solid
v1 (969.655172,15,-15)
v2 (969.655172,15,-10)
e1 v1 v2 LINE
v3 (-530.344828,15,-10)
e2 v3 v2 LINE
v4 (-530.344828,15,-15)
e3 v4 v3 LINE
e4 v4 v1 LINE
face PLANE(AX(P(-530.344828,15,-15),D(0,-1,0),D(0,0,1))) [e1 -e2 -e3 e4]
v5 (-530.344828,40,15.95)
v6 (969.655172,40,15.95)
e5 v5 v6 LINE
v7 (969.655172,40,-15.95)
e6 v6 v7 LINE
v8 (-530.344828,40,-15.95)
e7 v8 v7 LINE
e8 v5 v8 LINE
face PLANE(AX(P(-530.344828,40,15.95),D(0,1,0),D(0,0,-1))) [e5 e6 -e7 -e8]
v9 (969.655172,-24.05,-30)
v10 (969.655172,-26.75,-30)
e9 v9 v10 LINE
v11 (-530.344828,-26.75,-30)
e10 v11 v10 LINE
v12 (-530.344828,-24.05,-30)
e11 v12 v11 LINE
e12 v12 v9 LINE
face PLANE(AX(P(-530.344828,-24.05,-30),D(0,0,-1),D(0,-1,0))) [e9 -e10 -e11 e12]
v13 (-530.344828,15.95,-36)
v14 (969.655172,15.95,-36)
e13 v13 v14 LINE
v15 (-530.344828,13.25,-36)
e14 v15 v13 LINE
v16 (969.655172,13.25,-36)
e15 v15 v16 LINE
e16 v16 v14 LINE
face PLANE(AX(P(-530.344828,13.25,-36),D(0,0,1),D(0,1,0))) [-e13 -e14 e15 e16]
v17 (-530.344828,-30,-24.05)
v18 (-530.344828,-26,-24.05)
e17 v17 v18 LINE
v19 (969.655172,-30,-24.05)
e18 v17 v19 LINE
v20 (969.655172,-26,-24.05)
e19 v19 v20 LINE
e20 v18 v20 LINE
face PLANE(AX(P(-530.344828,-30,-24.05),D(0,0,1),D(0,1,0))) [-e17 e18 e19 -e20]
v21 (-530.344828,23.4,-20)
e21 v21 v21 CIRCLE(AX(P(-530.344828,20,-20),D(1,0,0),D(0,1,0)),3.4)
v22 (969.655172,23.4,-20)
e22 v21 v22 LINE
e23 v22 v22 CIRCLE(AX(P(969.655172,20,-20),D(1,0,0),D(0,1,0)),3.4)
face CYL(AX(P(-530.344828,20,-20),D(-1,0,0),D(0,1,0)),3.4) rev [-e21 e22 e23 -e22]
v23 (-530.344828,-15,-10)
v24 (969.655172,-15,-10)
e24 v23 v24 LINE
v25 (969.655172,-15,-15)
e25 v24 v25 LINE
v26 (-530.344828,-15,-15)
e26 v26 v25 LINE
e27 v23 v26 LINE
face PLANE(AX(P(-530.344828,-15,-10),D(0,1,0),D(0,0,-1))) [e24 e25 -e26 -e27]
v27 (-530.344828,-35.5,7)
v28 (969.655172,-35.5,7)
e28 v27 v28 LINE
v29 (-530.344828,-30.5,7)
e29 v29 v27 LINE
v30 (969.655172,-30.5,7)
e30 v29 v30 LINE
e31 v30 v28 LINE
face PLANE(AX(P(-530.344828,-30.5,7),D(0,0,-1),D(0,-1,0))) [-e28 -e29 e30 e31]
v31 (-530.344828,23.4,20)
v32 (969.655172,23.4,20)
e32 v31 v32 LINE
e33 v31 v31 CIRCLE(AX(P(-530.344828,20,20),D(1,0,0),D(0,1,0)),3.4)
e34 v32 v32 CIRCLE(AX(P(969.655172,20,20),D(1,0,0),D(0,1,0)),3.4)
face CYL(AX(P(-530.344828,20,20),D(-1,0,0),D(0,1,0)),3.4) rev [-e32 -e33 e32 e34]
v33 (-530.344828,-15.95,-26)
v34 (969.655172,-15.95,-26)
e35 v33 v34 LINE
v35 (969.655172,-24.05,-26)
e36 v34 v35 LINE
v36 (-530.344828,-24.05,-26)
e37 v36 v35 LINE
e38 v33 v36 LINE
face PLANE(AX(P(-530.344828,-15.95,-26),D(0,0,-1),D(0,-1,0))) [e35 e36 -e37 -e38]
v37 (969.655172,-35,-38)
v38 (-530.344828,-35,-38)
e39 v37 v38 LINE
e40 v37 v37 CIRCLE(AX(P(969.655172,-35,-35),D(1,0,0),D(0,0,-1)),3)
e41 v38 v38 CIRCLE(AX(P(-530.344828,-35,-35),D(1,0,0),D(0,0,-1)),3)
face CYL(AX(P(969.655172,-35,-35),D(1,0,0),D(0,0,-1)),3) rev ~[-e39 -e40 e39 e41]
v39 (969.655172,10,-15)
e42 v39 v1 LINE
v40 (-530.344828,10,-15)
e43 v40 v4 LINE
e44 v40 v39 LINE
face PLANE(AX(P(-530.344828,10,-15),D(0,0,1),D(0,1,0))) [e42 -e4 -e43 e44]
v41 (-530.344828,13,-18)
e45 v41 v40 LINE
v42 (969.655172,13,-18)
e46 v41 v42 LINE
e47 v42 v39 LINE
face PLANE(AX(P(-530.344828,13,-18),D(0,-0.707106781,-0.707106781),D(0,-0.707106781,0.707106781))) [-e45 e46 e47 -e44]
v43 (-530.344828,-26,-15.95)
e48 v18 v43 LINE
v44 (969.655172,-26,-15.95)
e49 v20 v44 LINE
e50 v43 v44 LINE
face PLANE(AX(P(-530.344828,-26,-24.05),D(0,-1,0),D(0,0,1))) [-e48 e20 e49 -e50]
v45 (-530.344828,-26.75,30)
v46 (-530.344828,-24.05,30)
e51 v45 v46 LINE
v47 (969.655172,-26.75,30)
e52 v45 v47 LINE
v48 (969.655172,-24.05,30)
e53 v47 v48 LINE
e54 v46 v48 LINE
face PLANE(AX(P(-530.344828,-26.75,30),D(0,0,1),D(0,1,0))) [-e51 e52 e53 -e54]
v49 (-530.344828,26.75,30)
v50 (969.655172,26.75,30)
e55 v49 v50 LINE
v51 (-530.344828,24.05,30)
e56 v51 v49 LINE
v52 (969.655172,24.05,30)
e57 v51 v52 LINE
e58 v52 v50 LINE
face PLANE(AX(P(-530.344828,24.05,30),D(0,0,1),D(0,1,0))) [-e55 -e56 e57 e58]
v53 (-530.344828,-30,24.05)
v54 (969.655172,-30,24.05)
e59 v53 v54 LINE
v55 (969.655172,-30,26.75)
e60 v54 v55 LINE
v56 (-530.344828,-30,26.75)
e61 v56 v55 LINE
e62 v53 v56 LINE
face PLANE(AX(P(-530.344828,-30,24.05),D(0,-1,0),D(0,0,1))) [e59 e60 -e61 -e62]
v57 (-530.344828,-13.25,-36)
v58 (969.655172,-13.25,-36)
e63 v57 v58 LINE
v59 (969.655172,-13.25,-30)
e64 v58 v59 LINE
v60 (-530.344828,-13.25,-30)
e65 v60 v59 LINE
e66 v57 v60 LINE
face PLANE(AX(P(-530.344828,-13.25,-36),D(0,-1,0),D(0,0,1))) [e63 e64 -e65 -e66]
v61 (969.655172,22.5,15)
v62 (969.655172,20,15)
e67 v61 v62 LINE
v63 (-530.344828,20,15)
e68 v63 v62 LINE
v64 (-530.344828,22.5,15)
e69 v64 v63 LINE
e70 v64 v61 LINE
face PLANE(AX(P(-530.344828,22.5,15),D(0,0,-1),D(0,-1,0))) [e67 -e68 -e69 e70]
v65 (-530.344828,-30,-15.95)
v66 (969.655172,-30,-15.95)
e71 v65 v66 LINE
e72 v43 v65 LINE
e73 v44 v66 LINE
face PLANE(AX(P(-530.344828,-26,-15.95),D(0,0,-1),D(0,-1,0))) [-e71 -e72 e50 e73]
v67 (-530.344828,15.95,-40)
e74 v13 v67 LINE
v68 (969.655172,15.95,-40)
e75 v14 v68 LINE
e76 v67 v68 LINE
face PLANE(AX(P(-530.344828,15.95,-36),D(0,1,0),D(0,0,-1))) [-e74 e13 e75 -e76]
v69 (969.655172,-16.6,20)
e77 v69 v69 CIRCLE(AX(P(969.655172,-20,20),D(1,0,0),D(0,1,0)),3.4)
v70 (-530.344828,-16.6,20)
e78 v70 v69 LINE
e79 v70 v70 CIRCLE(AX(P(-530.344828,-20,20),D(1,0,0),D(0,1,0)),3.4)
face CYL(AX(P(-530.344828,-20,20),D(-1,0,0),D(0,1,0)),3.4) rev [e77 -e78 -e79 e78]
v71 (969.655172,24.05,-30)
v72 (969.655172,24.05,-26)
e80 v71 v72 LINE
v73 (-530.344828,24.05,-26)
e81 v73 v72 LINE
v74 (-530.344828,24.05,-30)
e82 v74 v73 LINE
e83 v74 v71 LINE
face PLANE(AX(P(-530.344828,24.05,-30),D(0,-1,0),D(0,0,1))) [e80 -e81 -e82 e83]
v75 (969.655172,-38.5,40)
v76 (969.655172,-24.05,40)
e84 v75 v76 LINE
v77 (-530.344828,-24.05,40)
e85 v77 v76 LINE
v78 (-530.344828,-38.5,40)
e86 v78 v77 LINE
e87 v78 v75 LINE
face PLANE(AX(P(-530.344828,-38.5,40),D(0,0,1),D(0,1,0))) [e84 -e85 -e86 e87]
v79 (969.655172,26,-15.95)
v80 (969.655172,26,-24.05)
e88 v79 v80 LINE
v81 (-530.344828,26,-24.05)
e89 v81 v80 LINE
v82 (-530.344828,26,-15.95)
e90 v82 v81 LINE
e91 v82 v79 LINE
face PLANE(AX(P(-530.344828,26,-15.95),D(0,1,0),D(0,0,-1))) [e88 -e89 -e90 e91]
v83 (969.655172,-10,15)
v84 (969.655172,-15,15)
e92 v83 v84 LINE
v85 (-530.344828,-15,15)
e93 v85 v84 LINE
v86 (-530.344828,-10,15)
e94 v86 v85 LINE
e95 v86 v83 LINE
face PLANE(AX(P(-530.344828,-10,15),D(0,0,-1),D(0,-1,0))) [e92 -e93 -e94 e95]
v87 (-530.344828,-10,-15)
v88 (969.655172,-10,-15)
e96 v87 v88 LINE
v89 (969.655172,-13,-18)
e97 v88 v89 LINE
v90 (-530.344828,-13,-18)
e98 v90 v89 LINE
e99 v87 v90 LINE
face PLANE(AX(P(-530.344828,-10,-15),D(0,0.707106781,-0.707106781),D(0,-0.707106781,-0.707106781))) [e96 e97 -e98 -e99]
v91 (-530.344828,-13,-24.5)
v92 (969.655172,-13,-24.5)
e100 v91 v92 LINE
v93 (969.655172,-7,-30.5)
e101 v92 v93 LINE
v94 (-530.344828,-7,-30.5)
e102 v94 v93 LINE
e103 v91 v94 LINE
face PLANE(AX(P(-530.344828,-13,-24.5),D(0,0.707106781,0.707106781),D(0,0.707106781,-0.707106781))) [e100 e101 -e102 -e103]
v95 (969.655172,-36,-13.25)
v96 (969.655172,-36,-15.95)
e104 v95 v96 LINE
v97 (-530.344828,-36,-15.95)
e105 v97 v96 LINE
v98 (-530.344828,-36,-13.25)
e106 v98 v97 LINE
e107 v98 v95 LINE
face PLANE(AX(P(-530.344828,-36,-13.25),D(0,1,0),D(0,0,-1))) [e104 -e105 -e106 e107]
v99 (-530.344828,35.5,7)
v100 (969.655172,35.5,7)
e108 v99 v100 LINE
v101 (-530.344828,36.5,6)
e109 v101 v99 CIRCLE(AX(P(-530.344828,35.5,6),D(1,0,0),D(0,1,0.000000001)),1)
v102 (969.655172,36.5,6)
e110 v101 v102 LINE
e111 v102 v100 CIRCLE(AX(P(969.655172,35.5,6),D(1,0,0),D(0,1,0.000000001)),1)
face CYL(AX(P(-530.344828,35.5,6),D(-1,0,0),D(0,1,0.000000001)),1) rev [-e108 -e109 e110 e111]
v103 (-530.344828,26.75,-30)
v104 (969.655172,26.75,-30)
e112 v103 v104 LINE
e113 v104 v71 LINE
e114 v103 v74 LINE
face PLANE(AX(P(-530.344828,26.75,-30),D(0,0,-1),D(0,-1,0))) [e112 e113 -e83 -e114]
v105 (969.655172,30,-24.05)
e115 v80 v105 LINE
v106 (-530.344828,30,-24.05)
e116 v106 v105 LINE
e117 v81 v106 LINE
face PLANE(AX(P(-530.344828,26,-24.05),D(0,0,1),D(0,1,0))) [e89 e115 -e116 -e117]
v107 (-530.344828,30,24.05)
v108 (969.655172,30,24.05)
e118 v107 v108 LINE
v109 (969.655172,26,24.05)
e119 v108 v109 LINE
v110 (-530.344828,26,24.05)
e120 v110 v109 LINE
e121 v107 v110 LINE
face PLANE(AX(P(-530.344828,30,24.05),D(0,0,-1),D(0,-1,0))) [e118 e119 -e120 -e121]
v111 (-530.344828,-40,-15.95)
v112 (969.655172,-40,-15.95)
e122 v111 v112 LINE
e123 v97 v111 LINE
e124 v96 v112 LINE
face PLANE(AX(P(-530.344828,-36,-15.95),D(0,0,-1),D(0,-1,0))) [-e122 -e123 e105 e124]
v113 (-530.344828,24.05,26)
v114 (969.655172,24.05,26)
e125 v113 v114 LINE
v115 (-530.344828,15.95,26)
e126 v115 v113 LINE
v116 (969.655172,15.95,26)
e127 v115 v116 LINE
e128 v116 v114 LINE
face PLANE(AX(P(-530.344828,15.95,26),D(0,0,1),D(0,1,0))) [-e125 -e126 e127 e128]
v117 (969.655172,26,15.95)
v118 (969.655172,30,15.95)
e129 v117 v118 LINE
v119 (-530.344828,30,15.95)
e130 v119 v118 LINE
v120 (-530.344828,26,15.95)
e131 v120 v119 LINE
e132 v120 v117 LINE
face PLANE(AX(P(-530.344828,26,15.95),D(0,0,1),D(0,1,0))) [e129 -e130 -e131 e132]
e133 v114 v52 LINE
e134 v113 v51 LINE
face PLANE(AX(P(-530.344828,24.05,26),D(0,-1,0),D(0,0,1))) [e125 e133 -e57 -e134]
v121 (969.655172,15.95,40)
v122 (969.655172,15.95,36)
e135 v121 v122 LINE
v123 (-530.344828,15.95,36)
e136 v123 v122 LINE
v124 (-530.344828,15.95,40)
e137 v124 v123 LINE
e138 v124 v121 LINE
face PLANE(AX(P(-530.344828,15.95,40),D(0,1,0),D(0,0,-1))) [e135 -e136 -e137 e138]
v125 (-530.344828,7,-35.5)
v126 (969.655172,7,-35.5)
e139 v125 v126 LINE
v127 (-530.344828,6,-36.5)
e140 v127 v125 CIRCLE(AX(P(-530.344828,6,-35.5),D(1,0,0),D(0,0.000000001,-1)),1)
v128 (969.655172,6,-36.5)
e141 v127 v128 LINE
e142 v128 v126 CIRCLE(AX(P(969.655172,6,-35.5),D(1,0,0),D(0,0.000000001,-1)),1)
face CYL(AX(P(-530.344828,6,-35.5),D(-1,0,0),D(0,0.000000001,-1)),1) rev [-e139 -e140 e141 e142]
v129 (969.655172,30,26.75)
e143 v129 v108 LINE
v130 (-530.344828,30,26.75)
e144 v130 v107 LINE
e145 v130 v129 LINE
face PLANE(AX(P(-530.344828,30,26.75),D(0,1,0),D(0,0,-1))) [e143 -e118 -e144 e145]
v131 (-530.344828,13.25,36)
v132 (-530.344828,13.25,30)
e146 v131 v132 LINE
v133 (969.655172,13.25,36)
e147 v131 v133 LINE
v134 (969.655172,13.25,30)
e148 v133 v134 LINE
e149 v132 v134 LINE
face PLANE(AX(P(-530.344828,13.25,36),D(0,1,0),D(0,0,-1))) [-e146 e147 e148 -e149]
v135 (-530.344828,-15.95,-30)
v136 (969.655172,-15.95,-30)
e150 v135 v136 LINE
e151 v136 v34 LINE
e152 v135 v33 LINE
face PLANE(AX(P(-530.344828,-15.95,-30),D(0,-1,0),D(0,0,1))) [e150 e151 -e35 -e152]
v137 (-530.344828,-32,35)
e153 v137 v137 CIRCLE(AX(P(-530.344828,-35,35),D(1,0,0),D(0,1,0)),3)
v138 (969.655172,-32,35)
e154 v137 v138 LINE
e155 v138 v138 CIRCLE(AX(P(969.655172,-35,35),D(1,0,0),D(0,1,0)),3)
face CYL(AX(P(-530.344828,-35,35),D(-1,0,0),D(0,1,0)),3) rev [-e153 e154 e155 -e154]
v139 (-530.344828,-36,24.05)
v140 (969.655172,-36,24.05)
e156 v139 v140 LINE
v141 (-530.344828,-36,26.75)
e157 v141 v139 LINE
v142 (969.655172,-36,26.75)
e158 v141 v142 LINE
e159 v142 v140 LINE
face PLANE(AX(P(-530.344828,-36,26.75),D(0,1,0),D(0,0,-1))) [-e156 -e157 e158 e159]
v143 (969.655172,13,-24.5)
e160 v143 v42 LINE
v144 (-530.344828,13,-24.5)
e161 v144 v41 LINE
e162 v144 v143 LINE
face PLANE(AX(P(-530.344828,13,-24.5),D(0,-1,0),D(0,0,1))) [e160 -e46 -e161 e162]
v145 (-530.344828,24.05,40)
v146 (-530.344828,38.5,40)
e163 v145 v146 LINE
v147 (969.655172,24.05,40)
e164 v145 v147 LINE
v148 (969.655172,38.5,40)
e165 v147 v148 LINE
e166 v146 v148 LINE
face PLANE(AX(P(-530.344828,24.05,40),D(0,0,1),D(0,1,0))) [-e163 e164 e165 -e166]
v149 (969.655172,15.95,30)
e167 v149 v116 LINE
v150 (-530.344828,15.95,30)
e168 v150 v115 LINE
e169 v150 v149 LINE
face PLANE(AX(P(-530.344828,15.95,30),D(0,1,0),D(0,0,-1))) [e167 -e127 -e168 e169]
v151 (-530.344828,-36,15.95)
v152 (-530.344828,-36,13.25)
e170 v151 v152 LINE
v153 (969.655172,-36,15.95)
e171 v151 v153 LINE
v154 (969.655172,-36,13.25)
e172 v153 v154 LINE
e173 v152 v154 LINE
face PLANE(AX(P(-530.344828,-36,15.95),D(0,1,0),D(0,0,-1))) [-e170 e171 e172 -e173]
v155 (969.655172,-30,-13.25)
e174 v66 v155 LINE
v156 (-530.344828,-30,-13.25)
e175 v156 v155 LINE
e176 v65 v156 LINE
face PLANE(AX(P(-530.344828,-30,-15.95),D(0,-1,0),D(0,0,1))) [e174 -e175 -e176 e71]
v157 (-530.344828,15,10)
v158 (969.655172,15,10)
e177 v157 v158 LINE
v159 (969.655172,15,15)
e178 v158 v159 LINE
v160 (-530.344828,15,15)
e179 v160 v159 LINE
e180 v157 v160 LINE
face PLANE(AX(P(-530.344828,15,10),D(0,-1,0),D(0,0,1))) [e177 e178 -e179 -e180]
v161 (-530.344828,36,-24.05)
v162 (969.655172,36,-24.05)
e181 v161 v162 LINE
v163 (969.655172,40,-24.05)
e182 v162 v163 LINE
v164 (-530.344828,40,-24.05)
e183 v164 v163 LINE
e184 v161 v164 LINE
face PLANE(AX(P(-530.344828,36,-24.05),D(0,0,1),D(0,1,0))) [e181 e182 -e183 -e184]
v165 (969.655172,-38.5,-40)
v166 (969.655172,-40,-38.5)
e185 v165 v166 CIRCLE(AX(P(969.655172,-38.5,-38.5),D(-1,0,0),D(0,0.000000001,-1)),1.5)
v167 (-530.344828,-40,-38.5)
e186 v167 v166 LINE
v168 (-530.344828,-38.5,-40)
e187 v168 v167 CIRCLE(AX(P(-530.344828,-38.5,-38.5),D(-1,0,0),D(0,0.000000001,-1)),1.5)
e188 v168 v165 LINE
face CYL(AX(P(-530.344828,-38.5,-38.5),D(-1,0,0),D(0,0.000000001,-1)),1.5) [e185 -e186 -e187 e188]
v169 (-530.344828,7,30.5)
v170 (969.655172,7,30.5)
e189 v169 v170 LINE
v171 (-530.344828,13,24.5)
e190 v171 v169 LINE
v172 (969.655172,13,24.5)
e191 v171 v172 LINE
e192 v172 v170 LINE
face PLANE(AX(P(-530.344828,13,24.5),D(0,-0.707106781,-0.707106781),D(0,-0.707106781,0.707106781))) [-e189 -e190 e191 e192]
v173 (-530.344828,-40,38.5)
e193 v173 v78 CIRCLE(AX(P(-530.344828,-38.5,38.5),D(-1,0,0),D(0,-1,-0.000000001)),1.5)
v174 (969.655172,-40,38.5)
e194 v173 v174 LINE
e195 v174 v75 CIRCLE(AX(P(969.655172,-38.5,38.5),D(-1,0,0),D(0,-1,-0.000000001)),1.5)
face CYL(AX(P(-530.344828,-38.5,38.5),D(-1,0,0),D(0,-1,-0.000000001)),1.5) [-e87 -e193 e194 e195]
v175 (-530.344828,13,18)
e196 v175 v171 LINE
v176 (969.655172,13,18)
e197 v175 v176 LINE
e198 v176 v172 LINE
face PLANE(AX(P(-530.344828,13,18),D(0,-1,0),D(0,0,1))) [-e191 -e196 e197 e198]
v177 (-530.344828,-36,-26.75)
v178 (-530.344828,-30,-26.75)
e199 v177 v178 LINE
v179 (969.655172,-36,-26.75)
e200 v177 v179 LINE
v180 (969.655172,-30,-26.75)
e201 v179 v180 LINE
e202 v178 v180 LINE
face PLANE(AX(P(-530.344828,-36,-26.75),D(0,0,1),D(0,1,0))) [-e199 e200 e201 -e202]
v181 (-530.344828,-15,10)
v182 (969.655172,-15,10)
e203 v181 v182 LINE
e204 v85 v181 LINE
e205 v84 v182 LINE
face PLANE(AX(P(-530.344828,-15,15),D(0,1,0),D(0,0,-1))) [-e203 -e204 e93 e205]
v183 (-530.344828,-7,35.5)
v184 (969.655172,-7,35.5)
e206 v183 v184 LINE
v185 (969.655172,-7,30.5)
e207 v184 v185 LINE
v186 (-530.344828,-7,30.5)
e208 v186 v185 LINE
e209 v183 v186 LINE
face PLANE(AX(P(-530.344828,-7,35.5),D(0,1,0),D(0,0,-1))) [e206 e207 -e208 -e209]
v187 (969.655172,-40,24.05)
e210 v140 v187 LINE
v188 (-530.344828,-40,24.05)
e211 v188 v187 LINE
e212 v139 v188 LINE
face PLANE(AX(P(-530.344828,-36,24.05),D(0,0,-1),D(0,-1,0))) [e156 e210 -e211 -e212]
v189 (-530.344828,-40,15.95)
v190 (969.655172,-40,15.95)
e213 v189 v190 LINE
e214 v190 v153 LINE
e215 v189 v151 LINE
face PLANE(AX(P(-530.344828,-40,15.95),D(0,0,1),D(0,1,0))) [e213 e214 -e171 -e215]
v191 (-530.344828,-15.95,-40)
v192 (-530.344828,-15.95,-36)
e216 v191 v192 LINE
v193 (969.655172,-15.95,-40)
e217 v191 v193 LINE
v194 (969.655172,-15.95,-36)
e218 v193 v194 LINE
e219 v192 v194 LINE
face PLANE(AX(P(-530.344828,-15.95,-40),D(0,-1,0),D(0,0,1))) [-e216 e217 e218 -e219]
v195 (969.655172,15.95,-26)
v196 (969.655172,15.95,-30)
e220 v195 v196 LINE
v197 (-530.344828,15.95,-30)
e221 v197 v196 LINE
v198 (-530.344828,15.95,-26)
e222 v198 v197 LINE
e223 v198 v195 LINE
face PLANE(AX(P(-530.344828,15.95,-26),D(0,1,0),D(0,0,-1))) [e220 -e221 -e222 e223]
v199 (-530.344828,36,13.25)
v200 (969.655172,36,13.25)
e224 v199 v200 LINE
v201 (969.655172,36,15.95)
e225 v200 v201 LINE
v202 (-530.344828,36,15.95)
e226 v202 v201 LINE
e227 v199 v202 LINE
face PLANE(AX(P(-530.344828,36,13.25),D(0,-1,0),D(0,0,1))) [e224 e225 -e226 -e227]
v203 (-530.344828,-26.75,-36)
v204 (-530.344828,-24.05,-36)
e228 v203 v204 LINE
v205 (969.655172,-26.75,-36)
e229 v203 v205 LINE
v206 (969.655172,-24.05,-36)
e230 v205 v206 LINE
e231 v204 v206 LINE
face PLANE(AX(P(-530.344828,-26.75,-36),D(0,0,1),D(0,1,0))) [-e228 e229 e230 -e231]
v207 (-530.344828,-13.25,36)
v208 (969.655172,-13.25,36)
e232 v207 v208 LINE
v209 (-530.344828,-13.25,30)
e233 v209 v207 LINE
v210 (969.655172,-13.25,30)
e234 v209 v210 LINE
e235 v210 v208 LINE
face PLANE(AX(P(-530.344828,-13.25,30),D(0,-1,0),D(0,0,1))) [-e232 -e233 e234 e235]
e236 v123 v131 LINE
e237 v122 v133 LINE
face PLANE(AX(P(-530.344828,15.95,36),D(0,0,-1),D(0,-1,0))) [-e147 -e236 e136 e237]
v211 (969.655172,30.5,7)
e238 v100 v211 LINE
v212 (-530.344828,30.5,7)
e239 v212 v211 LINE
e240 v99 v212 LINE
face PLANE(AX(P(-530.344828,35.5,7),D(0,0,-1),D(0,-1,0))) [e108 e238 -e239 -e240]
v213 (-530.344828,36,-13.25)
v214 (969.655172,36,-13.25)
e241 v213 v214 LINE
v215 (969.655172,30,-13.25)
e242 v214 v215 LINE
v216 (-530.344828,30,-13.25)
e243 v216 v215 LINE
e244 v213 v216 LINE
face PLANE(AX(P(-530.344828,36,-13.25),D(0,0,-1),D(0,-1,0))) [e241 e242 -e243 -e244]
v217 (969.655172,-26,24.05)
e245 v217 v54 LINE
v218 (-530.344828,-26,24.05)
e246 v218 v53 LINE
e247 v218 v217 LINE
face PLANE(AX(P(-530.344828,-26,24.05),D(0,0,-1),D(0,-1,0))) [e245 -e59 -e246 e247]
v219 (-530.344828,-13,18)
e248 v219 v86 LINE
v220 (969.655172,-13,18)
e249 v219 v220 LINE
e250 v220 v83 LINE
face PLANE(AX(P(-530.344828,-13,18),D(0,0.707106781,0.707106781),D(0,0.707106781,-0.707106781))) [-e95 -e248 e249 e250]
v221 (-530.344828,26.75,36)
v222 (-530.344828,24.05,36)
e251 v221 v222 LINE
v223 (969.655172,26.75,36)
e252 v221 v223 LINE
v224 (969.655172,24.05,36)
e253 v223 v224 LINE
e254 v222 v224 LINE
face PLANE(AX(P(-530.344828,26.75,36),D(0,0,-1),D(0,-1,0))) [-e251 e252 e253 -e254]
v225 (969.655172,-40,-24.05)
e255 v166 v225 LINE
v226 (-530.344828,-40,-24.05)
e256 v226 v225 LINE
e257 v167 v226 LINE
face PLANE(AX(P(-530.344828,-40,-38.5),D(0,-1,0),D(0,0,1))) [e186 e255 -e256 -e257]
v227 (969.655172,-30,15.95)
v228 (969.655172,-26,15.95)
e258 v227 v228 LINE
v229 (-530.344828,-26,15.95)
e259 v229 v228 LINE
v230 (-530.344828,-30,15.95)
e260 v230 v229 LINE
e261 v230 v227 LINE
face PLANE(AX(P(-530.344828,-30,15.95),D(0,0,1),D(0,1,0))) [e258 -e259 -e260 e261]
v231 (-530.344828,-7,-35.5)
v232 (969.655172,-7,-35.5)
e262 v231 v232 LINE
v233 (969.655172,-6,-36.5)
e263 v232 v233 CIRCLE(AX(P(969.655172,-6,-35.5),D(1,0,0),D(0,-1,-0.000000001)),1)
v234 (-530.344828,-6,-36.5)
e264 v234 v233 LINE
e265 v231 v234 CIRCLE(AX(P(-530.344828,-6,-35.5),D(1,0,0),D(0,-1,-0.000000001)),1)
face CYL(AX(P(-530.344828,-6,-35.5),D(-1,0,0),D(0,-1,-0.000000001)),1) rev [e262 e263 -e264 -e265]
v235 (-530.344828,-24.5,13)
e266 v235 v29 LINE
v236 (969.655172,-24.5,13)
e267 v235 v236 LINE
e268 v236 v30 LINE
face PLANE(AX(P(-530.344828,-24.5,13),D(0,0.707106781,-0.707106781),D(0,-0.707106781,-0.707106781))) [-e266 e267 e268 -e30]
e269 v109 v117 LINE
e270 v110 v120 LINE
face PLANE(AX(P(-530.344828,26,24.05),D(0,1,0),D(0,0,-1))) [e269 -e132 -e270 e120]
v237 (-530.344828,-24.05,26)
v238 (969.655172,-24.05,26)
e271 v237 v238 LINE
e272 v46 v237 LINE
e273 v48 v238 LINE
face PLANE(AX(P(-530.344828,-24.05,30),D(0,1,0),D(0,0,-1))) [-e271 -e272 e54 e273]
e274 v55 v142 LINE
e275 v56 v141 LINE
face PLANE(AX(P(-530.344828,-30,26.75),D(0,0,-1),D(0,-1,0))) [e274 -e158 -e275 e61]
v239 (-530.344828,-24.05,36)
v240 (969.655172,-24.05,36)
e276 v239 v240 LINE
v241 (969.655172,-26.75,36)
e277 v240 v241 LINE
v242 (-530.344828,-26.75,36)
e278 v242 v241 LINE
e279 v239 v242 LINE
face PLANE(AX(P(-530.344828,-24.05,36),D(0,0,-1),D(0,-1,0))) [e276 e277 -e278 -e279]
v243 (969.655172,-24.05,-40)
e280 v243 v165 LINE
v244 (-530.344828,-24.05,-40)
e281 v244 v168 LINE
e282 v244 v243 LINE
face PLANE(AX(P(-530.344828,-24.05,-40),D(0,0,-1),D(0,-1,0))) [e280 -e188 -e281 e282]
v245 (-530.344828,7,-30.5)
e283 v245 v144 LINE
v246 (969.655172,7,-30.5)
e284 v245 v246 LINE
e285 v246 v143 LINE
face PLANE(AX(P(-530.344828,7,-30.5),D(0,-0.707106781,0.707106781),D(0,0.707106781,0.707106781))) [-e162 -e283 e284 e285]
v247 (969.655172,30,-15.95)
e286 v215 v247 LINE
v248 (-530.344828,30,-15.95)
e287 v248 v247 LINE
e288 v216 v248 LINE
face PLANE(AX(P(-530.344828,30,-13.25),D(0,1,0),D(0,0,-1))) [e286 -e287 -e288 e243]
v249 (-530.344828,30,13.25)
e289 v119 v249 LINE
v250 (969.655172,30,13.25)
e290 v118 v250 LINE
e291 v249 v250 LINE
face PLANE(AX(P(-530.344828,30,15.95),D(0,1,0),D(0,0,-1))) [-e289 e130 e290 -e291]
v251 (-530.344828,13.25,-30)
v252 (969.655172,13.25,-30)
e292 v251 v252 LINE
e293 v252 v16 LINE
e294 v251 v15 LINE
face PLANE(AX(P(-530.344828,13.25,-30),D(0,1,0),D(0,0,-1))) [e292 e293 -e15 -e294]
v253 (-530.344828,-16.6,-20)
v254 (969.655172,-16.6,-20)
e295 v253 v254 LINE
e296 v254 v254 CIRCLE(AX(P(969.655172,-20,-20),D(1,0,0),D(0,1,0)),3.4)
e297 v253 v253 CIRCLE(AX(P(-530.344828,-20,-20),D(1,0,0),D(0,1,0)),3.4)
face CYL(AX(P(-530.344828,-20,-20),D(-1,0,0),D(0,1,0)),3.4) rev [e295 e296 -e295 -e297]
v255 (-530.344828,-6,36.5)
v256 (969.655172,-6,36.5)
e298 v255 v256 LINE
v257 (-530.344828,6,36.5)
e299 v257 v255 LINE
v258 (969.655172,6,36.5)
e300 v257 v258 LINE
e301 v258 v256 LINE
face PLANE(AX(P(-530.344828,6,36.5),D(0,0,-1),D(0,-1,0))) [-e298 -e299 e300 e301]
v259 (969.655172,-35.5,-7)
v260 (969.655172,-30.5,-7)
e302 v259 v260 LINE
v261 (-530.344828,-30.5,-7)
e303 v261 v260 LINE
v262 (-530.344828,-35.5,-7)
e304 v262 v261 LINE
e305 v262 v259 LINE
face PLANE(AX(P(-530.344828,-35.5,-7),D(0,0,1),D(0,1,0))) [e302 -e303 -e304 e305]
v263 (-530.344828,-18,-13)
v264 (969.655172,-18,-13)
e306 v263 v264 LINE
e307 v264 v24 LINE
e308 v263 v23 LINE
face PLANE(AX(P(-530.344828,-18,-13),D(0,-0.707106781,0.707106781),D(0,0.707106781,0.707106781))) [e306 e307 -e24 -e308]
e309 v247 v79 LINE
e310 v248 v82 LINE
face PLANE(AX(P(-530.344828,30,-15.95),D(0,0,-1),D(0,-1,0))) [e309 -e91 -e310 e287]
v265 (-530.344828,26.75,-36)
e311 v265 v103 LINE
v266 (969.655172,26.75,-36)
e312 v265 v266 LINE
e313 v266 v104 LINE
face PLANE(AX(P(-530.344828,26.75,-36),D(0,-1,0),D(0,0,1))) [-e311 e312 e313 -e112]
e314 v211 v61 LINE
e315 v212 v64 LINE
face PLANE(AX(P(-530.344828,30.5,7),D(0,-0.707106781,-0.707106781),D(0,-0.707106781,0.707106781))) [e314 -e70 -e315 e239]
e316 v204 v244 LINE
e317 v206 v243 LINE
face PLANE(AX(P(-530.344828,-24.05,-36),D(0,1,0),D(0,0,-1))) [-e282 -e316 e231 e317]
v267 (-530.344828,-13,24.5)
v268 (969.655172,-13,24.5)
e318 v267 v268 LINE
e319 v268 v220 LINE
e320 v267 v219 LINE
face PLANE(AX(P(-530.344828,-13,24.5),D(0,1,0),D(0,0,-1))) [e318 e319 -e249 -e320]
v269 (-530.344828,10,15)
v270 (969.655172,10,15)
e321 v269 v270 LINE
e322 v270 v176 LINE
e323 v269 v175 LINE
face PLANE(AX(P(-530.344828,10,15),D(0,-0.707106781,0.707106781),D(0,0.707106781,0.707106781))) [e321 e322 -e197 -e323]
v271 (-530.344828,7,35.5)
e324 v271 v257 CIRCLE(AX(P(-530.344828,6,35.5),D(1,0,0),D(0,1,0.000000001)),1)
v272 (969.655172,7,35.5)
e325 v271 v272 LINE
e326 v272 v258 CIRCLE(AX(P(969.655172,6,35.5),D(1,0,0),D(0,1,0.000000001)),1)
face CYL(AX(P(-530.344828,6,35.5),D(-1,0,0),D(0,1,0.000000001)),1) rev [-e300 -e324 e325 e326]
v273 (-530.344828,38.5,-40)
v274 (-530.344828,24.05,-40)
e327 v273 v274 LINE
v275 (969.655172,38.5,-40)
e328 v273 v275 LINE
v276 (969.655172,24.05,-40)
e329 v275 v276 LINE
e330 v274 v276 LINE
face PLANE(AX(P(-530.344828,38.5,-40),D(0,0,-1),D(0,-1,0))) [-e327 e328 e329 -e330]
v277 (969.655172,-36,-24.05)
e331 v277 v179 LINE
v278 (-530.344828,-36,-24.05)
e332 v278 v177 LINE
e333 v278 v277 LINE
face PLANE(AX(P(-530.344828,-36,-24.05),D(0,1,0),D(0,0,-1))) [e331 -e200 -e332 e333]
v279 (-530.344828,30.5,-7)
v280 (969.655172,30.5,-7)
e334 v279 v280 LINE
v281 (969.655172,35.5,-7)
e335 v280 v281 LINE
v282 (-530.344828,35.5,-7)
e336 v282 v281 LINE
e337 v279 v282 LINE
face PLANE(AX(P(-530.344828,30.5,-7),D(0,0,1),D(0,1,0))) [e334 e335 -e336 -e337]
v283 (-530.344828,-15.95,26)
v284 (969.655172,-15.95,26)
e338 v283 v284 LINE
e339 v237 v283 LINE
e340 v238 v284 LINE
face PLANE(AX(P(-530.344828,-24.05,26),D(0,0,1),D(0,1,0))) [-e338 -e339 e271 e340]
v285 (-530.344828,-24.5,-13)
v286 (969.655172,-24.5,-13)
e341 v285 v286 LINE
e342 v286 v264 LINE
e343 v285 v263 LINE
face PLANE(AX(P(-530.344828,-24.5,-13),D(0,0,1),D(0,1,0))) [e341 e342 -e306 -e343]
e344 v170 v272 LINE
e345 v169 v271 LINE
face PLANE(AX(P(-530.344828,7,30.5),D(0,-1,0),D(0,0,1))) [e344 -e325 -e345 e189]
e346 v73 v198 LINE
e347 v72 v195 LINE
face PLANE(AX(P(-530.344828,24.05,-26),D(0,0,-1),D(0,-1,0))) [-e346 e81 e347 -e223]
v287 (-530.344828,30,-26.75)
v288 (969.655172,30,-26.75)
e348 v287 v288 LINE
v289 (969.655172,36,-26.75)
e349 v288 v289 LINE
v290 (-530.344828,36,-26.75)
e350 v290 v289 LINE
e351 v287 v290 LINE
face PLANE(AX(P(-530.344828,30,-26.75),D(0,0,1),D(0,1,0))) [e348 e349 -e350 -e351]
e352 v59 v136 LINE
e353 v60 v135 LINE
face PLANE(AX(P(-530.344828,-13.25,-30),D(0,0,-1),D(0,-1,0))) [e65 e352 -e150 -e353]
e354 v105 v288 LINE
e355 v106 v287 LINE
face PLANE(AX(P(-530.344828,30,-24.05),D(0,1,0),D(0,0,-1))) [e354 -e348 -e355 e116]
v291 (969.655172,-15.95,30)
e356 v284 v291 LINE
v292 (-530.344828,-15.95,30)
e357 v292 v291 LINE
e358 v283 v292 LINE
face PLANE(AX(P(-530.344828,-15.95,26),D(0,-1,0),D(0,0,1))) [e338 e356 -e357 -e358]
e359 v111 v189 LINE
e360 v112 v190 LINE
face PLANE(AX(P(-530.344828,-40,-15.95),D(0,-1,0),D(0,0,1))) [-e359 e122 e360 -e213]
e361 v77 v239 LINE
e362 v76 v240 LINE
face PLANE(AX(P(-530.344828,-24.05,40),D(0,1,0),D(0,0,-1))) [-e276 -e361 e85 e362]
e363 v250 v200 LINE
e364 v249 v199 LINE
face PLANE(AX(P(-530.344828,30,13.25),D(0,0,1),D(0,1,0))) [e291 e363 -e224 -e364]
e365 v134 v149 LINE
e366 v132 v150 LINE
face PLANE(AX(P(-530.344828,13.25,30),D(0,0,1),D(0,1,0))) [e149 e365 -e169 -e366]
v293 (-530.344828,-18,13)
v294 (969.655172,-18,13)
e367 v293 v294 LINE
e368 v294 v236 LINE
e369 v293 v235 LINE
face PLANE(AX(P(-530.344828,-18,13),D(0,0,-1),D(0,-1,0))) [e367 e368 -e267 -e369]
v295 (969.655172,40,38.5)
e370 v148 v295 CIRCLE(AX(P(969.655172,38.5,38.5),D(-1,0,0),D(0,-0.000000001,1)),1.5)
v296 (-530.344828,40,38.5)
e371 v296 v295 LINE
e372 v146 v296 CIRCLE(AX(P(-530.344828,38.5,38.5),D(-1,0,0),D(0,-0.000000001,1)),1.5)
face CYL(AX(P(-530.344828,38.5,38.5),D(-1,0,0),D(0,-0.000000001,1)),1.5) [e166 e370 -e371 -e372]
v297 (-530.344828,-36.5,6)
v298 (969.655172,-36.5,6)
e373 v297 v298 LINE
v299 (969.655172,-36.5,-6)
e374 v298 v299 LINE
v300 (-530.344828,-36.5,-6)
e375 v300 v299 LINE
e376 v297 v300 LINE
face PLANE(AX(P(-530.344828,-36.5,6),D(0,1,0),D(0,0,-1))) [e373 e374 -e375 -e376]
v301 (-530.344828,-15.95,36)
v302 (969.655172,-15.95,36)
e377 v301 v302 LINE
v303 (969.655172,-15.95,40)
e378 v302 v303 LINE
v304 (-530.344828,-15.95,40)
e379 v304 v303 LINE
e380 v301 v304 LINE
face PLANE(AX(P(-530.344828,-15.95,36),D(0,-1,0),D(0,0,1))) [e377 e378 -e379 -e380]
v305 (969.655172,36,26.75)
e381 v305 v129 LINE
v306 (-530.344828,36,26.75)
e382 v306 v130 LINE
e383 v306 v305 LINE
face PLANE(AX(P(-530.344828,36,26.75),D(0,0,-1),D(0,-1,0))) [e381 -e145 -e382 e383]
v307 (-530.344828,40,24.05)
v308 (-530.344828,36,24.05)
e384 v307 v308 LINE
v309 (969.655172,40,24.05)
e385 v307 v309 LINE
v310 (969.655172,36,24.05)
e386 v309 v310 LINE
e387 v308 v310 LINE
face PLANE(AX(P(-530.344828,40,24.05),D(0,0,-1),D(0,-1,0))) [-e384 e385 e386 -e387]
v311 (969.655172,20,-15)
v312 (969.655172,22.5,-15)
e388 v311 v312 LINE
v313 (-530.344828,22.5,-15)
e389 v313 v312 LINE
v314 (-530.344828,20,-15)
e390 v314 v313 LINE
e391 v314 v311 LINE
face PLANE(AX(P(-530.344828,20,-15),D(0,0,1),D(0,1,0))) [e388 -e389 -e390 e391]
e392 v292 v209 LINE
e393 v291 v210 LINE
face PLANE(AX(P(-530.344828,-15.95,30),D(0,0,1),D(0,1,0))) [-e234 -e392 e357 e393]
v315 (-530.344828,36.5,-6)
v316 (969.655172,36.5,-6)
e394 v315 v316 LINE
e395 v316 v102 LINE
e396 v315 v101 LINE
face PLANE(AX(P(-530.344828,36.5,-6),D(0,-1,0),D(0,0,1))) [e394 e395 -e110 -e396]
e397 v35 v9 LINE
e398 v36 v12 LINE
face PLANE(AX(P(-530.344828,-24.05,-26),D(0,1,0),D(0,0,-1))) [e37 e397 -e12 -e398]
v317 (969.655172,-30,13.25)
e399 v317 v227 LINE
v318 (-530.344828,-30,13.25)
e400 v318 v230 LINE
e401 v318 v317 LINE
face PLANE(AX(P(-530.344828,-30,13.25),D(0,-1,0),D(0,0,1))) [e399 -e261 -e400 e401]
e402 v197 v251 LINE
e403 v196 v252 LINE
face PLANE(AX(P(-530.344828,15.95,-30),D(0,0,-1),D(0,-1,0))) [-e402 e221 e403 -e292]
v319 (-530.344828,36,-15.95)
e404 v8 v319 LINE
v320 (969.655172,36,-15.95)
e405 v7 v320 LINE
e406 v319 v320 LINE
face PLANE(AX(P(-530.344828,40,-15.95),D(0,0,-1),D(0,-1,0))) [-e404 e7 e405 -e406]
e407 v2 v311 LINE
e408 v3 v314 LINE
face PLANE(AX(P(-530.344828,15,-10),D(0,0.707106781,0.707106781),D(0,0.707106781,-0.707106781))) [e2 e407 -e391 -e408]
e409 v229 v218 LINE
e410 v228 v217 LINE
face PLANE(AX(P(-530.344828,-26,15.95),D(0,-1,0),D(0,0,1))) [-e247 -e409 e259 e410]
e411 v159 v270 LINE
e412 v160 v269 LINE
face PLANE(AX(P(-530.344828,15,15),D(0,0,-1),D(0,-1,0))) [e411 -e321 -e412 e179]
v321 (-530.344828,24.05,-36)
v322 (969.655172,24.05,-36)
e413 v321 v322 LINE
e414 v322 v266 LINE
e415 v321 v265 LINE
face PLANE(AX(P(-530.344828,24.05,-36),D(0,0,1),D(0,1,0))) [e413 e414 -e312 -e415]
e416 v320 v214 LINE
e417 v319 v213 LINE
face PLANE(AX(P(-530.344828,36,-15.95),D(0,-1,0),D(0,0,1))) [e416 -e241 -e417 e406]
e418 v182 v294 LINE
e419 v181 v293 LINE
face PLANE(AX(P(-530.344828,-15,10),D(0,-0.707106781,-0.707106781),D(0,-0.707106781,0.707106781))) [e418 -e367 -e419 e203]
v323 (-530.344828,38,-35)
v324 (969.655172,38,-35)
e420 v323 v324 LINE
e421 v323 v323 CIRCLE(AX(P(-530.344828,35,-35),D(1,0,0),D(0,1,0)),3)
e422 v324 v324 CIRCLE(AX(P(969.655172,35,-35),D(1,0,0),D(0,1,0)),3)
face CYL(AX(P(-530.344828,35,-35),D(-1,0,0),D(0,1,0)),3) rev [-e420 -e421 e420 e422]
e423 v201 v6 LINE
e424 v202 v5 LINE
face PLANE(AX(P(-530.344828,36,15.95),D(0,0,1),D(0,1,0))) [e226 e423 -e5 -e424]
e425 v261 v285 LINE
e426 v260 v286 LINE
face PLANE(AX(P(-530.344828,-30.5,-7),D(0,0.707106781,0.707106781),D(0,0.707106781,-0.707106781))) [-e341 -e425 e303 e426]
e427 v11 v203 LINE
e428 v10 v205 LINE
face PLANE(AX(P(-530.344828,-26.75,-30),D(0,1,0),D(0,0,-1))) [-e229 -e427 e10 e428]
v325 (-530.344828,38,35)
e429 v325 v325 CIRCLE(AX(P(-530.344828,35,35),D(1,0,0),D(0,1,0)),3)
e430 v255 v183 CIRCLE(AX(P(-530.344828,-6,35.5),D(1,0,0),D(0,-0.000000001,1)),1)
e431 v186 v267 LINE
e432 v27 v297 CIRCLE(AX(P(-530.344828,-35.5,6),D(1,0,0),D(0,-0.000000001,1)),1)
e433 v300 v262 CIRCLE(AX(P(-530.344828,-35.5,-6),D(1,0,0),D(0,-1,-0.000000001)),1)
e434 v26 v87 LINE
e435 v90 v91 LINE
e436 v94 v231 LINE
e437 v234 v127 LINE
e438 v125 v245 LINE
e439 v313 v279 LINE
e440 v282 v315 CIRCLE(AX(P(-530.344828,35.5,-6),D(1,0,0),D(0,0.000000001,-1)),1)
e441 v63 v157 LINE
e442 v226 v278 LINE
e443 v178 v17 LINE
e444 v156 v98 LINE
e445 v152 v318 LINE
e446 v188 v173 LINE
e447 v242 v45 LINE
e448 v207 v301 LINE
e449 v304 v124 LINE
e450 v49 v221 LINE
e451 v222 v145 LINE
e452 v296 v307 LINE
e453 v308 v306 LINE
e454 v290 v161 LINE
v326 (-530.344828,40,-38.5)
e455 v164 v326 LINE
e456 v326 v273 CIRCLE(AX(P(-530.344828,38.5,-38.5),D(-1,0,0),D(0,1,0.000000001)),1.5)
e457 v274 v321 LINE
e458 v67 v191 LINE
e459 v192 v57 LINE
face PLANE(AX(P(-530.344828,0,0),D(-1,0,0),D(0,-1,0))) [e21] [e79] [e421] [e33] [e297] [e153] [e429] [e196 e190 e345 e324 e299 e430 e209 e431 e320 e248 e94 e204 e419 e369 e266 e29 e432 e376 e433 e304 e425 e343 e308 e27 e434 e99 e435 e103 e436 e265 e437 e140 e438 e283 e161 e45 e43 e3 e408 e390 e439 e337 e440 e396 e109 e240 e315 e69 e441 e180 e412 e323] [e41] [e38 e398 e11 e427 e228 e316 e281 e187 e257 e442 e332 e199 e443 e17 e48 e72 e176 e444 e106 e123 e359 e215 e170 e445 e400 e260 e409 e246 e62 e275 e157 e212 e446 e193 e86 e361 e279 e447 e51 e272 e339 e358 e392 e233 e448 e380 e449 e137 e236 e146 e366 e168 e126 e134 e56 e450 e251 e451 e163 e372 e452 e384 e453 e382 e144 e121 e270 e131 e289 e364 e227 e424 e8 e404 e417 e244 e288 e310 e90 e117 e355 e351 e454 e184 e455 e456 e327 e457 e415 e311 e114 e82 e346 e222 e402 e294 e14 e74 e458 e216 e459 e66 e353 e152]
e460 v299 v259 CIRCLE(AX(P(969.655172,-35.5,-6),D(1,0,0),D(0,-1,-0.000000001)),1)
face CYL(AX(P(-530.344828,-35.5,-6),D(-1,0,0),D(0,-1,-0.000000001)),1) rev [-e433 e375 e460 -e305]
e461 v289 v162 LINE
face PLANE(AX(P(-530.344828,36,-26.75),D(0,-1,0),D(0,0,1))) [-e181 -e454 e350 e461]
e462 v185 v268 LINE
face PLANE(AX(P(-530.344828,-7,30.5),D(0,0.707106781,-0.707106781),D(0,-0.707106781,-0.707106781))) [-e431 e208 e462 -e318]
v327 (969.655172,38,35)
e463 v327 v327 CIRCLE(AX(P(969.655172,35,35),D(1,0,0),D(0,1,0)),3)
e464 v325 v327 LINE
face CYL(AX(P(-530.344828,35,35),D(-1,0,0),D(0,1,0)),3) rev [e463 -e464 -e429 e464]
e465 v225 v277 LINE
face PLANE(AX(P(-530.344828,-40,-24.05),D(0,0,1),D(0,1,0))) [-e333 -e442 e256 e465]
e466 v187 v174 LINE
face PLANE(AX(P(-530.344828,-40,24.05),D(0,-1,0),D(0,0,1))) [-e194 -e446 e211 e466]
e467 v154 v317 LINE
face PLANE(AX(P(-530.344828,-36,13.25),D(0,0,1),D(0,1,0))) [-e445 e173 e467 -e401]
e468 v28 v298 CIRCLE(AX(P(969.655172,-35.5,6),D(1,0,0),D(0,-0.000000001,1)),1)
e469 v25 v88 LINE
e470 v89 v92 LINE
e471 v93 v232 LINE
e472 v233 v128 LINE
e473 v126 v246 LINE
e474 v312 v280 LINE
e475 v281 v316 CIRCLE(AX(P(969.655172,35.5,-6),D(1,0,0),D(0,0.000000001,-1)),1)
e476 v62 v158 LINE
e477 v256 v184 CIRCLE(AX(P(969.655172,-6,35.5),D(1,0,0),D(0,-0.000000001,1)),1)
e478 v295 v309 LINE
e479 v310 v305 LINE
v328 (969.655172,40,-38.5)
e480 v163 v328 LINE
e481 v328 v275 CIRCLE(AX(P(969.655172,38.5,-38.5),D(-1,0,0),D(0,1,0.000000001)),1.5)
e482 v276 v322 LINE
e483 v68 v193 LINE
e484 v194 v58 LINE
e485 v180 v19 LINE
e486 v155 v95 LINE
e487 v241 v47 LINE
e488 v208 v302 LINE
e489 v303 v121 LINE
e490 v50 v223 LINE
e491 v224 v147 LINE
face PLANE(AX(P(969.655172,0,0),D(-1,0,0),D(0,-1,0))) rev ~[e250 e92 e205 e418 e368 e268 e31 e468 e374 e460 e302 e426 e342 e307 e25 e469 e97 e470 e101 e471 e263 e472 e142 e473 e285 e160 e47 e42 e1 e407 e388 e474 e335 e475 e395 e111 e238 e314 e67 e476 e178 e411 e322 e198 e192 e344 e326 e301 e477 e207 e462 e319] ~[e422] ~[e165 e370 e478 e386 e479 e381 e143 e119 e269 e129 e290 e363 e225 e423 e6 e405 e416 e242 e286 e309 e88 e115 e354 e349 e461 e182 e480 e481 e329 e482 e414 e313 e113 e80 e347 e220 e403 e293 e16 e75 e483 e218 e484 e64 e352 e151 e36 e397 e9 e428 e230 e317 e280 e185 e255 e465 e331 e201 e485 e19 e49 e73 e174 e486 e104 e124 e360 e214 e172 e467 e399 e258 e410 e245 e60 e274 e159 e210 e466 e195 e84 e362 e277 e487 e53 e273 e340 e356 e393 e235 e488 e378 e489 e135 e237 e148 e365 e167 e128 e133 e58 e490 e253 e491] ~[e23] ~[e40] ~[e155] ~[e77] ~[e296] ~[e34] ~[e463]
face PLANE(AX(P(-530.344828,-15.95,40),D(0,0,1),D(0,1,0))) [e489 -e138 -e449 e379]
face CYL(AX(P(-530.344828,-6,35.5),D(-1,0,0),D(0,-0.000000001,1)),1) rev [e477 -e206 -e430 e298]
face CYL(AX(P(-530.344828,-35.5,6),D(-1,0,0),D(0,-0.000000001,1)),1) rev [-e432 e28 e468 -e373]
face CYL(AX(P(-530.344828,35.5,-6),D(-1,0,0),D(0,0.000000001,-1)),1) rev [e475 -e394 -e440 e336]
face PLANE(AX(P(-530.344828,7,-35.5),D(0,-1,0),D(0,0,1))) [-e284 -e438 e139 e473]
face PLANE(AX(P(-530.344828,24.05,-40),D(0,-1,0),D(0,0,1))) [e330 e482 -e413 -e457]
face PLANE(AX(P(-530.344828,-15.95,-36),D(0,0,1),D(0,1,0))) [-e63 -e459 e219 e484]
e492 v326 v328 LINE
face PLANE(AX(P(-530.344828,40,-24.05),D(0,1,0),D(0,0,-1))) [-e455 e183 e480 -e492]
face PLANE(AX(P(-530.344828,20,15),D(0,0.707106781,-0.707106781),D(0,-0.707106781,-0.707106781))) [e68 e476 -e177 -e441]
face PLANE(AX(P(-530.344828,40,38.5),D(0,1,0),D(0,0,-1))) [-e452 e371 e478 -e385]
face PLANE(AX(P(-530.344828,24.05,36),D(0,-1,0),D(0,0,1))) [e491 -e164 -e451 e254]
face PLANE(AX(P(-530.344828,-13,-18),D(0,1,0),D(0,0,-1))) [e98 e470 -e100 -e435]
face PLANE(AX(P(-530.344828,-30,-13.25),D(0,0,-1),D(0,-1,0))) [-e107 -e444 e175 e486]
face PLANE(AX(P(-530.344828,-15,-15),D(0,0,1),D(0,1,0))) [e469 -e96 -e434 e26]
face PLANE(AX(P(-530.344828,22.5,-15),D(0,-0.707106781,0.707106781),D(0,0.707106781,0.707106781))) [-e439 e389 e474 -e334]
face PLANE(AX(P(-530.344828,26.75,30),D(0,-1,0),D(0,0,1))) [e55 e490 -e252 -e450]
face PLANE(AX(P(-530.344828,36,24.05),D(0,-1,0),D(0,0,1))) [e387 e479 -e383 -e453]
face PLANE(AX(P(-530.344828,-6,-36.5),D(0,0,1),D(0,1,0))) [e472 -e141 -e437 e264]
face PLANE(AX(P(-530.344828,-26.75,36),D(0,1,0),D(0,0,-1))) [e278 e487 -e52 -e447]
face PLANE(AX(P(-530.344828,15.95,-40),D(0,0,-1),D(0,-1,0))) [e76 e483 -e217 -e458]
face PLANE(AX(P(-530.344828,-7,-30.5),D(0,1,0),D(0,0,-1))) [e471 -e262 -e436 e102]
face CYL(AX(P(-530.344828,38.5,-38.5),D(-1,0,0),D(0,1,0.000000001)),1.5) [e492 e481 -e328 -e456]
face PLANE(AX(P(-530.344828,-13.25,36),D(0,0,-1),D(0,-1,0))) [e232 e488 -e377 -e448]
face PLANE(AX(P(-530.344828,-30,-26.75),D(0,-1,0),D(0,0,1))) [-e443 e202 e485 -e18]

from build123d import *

# Parameters (mm, degrees)
SKETCH1_R                                = 3.4
SKETCH1_R_2                              = 3
ALUMINUM_PROFILE_80_X_80G_X_R1_5_1_DEPTH = 1500
SKETCH10_R                               = 3
CUT_EXTRUDE1_DEPTH                       = 1502.066287677


with BuildPart() as part:
    # Sketch1 → Aluminum profile 80 X 80G X R1.5(1) (new body)
    with BuildSketch(Plane.YZ.offset(-530.344827586)):
        with BuildLine():
            Line((-24.05, 40), (-24.05, 36))
            Line((-24.05, 36), (-26.75, 36))
            Line((-26.75, 36), (-26.75, 30))
            Line((-26.75, 30), (-24.05, 30))
            Line((-24.05, 30), (-24.05, 26))
            Line((-24.05, 26), (-15.95, 26))
            Line((-15.95, 26), (-15.95, 30))
            Line((-15.95, 30), (-13.25, 30))
            Line((-13.25, 30), (-13.25, 36))
            Line((-13.25, 36), (-15.95, 36))
            Line((-15.95, 36), (-15.95, 40))
            Line((-15.95, 40), (15.95, 40))
            Line((15.95, 40), (15.95, 36))
            Line((15.95, 36), (13.25, 36))
            Line((13.25, 36), (13.25, 30))
            Line((13.25, 30), (15.95, 30))
            Line((15.95, 30), (15.95, 26))
            Line((15.95, 26), (24.05, 26))
            Line((24.05, 26), (24.05, 30))
            Line((24.05, 30), (26.75, 30))
            Line((26.75, 30), (26.75, 36))
            Line((26.75, 36), (24.05, 36))
            Line((24.05, 36), (24.05, 40))
            Line((24.05, 40), (38.5, 40))
            ThreePointArc((38.5, 40), (39.560660172, 39.560660172), (40, 38.5))
            Line((40, 38.5), (40, 24.05))
            Line((40, 24.05), (36, 24.05))
            Line((36, 24.05), (36, 26.75))
            Line((36, 26.75), (30, 26.75))
            Line((30, 26.75), (30, 24.05))
            Line((30, 24.05), (26, 24.05))
            Line((26, 24.05), (26, 15.95))
            Line((26, 15.95), (30, 15.95))
            Line((30, 15.95), (30, 13.25))
            Line((30, 13.25), (36, 13.25))
            Line((36, 13.25), (36, 15.95))
            Line((36, 15.95), (40, 15.95))
            Line((40, 15.95), (40, -15.95))
            Line((40, -15.95), (36, -15.95))
            Line((36, -15.95), (36, -13.25))
            Line((36, -13.25), (30, -13.25))
            Line((30, -13.25), (30, -15.95))
            Line((30, -15.95), (26, -15.95))
            Line((26, -15.95), (26, -24.05))
            Line((26, -24.05), (30, -24.05))
            Line((30, -24.05), (30, -26.75))
            Line((30, -26.75), (36, -26.75))
            Line((36, -26.75), (36, -24.05))
            Line((36, -24.05), (40, -24.05))
            Line((40, -24.05), (40, -38.5))
            ThreePointArc((40, -38.5), (39.560660172, -39.560660172), (38.5, -40))
            Line((38.5, -40), (24.05, -40))
            Line((24.05, -40), (24.05, -36))
            Line((24.05, -36), (26.75, -36))
            Line((26.75, -36), (26.75, -30))
            Line((26.75, -30), (24.05, -30))
            Line((24.05, -30), (24.05, -26))
            Line((24.05, -26), (15.95, -26))
            Line((15.95, -26), (15.95, -30))
            Line((15.95, -30), (13.25, -30))
            Line((13.25, -30), (13.25, -36))
            Line((13.25, -36), (15.95, -36))
            Line((15.95, -36), (15.95, -40))
            Line((15.95, -40), (-15.95, -40))
            Line((-15.95, -40), (-15.95, -36))
            Line((-15.95, -36), (-13.25, -36))
            Line((-13.25, -36), (-13.25, -30))
            Line((-13.25, -30), (-15.95, -30))
            Line((-15.95, -30), (-15.95, -26))
            Line((-15.95, -26), (-24.05, -26))
            Line((-24.05, -26), (-24.05, -30))
            Line((-24.05, -30), (-26.75, -30))
            Line((-26.75, -30), (-26.75, -36))
            Line((-26.75, -36), (-24.05, -36))
            Line((-24.05, -36), (-24.05, -40))
            Line((-24.05, -40), (-38.5, -40))
            ThreePointArc((-38.5, -40), (-39.560660172, -39.560660172), (-40, -38.5))
            Line((-40, -38.5), (-40, -24.05))
            Line((-40, -24.05), (-36, -24.05))
            Line((-36, -24.05), (-36, -26.75))
            Line((-36, -26.75), (-30, -26.75))
            Line((-30, -26.75), (-30, -24.05))
            Line((-30, -24.05), (-26, -24.05))
            Line((-26, -24.05), (-26, -15.95))
            Line((-26, -15.95), (-30, -15.95))
            Line((-30, -15.95), (-30, -13.25))
            Line((-30, -13.25), (-36, -13.25))
            Line((-36, -13.25), (-36, -15.95))
            Line((-36, -15.95), (-40, -15.95))
            Line((-40, -15.95), (-40, 15.95))
            Line((-40, 15.95), (-36, 15.95))
            Line((-36, 15.95), (-36, 13.25))
            Line((-36, 13.25), (-30, 13.25))
            Line((-30, 13.25), (-30, 15.95))
            Line((-30, 15.95), (-26, 15.95))
            Line((-26, 15.95), (-26, 24.05))
            Line((-26, 24.05), (-30, 24.05))
            Line((-30, 24.05), (-30, 26.75))
            Line((-30, 26.75), (-36, 26.75))
            Line((-36, 26.75), (-36, 24.05))
            Line((-36, 24.05), (-40, 24.05))
            Line((-40, 24.05), (-40, 38.5))
            ThreePointArc((-40, 38.5), (-39.560660172, 39.560660172), (-38.5, 40))
            Line((-38.5, 40), (-24.05, 40))
        make_face()
        with Locations((-20, 20)):
            Circle(SKETCH1_R, mode=Mode.SUBTRACT)
        with Locations((20, 20)):
            Circle(SKETCH1_R, mode=Mode.SUBTRACT)
        with Locations((20, -20)):
            Circle(SKETCH1_R, mode=Mode.SUBTRACT)
        with Locations((-20, -20)):
            Circle(SKETCH1_R, mode=Mode.SUBTRACT)
        with Locations((-35, 35)):
            Circle(SKETCH1_R_2, mode=Mode.SUBTRACT)
        with Locations((35, 35)):
            Circle(SKETCH1_R_2, mode=Mode.SUBTRACT)
        with Locations((35, -35)):
            Circle(SKETCH1_R_2, mode=Mode.SUBTRACT)
        with BuildLine():
            Line((-13, 18), (-10, 15))
            Line((-10, 15), (-15, 15))
            Line((-15, 15), (-15, 10))
            Line((-15, 10), (-18, 13))
            Line((-18, 13), (-24.5, 13))
            Line((-24.5, 13), (-30.5, 7))
            Line((-30.5, 7), (-35.5, 7))
            ThreePointArc((-35.5, 7), (-36.207106781, 6.707106781), (-36.5, 6))
            Line((-36.5, 6), (-36.5, -6))
            ThreePointArc((-36.5, -6), (-36.207106781, -6.707106781), (-35.5, -7))
            Line((-35.5, -7), (-30.5, -7))
            Line((-30.5, -7), (-24.5, -13))
            Line((-24.5, -13), (-18, -13))
            Line((-18, -13), (-15, -10))
            Line((-15, -10), (-15, -15))
            Line((-15, -15), (-10, -15))
            Line((-10, -15), (-13, -18))
            Line((-13, -18), (-13, -24.5))
            Line((-13, -24.5), (-7, -30.5))
            Line((-7, -30.5), (-7, -35.5))
            ThreePointArc((-7, -35.5), (-6.707106781, -36.207106781), (-6, -36.5))
            Line((-6, -36.5), (6, -36.5))
            ThreePointArc((6, -36.5), (6.707106781, -36.207106781), (7, -35.5))
            Line((7, -35.5), (7, -30.5))
            Line((7, -30.5), (13, -24.5))
            Line((13, -24.5), (13, -18))
            Line((13, -18), (10, -15))
            Line((10, -15), (15, -15))
            Line((15, -15), (15, -10))
            Line((15, -10), (20, -15))
            Line((20, -15), (22.5, -15))
            Line((22.5, -15), (30.5, -7))
            Line((30.5, -7), (35.5, -7))
            ThreePointArc((35.5, -7), (36.207106781, -6.707106781), (36.5, -6))
            Line((36.5, -6), (36.5, 6))
            ThreePointArc((36.5, 6), (36.207106781, 6.707106781), (35.5, 7))
            Line((35.5, 7), (30.5, 7))
            Line((30.5, 7), (22.5, 15))
            Line((22.5, 15), (20, 15))
            Line((20, 15), (15, 10))
            Line((15, 10), (15, 15))
            Line((15, 15), (10, 15))
            Line((10, 15), (13, 18))
            Line((13, 18), (13, 24.5))
            Line((13, 24.5), (7, 30.5))
            Line((7, 30.5), (7, 35.5))
            ThreePointArc((7, 35.5), (6.707106781, 36.207106781), (6, 36.5))
            Line((6, 36.5), (-6, 36.5))
            ThreePointArc((-6, 36.5), (-6.707106781, 36.207106781), (-7, 35.5))
            Line((-7, 35.5), (-7, 30.5))
            Line((-7, 30.5), (-13, 24.5))
            Line((-13, 24.5), (-13, 18))
        make_face(mode=Mode.SUBTRACT)
    extrude(amount=ALUMINUM_PROFILE_80_X_80G_X_R1_5_1_DEPTH)

    # Sketch10 → Cut-Extrude1 (cut, through all)
    with BuildSketch(Plane(origin=(969.655172414, 0, 0), x_dir=(0, 0, -1), z_dir=(1, 0, 0))):
        with Locations((35, -35)):
            Circle(SKETCH10_R)
    extrude(amount=-CUT_EXTRUDE1_DEPTH, mode=Mode.SUBTRACT)


solid = part.part
